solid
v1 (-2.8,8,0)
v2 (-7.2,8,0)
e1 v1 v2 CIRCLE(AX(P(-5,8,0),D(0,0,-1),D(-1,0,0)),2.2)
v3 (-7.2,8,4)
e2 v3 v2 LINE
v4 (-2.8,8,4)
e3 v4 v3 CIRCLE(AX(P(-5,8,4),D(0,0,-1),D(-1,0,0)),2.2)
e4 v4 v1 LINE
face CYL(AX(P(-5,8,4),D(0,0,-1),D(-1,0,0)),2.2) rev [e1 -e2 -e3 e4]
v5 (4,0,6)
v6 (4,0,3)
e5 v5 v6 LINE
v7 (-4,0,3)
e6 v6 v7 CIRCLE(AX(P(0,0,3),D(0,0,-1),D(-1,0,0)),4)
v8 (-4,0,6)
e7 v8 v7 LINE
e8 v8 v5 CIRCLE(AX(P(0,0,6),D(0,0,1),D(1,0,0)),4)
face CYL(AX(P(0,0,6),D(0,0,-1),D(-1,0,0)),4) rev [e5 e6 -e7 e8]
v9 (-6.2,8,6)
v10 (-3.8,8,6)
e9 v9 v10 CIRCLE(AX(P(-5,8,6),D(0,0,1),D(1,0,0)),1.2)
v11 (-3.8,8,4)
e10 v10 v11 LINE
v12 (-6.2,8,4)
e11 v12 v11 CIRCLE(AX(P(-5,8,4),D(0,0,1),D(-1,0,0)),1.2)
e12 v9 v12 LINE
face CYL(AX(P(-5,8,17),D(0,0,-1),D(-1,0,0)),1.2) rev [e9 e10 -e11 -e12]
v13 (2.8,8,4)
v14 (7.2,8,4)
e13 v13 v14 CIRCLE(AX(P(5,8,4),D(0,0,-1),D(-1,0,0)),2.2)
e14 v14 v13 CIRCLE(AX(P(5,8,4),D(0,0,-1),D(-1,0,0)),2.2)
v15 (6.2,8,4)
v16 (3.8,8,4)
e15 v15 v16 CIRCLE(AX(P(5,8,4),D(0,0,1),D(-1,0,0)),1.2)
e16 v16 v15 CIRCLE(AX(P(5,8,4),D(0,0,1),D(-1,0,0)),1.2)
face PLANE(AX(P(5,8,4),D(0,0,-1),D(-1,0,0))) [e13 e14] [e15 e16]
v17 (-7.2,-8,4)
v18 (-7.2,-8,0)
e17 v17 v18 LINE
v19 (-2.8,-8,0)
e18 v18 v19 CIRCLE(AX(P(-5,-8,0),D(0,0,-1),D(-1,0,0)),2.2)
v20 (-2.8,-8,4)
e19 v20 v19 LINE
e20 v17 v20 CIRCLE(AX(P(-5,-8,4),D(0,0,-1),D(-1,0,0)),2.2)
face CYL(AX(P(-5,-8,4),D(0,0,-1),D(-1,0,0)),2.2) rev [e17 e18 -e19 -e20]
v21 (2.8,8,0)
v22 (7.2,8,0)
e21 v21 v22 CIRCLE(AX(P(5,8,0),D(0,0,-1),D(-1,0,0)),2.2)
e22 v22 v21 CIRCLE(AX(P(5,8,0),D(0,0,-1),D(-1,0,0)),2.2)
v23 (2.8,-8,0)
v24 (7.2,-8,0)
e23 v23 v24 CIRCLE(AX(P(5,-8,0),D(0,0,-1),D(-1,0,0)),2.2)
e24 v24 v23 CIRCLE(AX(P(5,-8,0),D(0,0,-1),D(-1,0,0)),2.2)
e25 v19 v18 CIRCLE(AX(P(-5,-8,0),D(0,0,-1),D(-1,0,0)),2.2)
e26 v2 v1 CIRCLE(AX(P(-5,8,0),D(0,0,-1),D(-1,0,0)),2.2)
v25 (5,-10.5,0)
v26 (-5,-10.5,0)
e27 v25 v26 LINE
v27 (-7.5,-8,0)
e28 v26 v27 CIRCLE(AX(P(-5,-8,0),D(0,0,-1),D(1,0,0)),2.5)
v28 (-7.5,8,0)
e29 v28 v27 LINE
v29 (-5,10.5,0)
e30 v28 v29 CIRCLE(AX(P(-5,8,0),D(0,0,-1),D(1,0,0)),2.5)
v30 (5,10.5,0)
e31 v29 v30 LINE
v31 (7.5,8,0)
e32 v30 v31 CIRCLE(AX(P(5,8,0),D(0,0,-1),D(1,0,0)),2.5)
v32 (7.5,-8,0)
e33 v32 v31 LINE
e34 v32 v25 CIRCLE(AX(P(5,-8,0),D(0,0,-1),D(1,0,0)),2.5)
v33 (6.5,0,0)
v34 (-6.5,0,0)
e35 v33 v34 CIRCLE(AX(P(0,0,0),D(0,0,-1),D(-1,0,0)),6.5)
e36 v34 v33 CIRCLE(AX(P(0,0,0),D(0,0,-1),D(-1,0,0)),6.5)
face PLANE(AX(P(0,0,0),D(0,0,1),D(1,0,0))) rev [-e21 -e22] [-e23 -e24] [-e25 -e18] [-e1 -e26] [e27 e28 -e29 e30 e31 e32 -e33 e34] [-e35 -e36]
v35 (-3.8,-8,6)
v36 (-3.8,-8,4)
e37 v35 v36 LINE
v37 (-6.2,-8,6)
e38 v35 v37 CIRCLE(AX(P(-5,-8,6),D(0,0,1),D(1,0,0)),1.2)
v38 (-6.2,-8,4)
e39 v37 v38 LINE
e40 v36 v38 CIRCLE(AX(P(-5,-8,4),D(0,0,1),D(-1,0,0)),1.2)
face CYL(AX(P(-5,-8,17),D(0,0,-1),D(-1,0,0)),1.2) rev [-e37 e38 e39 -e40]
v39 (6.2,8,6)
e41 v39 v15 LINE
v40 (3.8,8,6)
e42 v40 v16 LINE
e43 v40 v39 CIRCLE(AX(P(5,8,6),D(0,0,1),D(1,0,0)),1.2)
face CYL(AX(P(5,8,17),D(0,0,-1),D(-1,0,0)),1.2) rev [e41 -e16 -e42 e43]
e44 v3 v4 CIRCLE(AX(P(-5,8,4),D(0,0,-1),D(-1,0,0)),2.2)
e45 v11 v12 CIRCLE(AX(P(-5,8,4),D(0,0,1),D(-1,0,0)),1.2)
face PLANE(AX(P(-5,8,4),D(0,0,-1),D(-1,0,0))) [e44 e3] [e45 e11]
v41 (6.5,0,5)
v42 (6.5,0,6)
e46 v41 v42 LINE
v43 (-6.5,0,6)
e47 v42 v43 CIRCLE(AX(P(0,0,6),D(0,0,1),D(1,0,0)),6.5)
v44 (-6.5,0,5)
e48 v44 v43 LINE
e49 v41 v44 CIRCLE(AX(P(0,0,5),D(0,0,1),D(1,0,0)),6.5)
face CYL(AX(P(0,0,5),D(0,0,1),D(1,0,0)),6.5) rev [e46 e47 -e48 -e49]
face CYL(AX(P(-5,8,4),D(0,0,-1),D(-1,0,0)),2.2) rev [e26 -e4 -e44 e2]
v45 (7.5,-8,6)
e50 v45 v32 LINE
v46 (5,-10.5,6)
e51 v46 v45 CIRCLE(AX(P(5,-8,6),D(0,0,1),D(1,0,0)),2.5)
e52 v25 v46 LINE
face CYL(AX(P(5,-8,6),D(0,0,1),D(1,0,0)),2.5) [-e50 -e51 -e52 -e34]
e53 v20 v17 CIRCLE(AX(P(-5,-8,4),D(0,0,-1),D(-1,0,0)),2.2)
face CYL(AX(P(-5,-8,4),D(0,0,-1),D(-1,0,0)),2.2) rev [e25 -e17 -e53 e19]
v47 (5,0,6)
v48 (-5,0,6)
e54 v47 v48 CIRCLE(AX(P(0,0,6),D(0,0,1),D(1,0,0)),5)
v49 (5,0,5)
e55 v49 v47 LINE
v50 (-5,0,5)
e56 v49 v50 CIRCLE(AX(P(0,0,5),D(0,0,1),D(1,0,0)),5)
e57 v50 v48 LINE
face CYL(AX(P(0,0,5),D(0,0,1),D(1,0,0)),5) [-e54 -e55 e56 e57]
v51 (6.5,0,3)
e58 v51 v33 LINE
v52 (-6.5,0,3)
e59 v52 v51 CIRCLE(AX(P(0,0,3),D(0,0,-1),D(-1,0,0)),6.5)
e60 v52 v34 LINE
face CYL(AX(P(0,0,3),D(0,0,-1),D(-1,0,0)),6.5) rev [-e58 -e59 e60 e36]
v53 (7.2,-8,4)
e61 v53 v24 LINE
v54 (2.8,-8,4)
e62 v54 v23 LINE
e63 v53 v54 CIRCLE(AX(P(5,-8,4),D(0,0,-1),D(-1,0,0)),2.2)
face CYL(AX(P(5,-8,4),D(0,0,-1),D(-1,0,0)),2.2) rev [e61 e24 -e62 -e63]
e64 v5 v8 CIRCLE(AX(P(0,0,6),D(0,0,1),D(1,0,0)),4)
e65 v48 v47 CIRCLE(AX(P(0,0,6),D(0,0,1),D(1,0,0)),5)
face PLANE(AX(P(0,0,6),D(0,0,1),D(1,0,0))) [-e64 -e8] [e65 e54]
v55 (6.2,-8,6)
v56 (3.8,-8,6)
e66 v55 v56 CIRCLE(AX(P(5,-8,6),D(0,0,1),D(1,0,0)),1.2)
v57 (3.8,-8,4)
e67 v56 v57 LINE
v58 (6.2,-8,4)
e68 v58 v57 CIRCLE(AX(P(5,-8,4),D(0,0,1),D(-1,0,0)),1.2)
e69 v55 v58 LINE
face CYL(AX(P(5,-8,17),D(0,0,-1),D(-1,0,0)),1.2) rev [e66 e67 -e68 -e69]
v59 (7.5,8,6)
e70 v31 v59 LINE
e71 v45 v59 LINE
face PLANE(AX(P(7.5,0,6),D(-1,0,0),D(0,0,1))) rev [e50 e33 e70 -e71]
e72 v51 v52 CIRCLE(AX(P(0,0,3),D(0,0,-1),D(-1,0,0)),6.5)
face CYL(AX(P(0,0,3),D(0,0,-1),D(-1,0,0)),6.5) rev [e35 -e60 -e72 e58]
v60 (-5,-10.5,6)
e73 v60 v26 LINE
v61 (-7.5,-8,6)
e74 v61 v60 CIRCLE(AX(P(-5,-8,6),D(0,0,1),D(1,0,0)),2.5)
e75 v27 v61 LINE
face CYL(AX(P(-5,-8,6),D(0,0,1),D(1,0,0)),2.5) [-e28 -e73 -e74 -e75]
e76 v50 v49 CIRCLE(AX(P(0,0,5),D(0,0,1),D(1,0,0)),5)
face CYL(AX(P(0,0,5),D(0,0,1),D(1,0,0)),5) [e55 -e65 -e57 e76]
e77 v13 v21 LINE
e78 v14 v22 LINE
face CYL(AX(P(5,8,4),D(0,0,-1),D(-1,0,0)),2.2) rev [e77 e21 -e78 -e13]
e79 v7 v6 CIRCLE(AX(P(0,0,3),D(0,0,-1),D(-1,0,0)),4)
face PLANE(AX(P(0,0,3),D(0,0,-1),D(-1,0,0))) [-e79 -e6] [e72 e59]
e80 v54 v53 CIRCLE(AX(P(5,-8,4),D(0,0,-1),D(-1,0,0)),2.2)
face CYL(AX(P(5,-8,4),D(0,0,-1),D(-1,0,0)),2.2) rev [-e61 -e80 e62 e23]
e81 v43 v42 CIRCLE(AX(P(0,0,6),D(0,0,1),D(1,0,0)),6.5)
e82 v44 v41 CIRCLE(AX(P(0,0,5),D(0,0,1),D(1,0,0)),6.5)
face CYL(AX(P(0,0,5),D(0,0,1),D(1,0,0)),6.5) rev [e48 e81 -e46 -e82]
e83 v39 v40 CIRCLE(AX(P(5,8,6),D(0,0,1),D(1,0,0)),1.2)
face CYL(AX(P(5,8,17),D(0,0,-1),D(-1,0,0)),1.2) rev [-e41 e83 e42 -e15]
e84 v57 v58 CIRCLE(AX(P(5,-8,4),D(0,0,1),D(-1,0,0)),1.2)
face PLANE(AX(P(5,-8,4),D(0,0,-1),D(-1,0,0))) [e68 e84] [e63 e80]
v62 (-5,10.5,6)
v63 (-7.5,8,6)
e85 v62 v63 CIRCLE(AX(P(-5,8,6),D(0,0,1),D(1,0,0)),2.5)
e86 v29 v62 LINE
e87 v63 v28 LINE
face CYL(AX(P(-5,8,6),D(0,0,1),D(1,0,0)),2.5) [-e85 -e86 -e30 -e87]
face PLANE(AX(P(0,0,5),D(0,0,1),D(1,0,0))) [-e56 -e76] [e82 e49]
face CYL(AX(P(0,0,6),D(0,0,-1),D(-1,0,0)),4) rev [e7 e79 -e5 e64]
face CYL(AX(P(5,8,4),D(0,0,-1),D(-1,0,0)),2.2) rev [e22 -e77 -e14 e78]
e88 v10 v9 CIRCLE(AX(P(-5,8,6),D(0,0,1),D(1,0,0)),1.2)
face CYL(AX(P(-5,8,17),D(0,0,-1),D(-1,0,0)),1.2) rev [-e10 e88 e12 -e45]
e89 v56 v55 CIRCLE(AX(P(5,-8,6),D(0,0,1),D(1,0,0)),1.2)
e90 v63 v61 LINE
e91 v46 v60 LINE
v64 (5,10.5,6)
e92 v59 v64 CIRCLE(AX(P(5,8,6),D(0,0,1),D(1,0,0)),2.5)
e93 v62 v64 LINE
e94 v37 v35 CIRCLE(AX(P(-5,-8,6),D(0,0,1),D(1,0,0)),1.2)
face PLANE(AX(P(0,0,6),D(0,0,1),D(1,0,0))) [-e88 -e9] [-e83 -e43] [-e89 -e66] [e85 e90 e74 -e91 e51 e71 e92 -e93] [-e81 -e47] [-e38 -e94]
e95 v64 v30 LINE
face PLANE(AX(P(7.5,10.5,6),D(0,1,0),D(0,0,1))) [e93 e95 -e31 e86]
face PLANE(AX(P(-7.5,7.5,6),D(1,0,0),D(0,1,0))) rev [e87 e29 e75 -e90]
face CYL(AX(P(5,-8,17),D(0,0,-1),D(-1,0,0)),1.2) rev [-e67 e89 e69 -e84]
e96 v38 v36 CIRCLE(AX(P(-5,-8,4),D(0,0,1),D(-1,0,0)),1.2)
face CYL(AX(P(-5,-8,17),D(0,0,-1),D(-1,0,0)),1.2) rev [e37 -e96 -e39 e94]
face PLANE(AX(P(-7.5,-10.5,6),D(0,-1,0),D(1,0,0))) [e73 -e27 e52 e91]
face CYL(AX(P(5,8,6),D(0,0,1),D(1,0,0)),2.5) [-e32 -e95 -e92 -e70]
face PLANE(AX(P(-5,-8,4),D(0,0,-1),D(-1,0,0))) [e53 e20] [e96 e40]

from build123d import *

# Parameters (mm, degrees)
SKETCH1_R           = 4
BOSS_EXTRUDE1_DEPTH = 6
SKETCH3_R           = 6.5
CUT_EXTRUDE2_DEPTH  = 3
CUT_EXTRUDE3_START  = -1
SKETCH4_R           = 6.5
SKETCH4_R_2         = 5
CUT_EXTRUDE3_DEPTH  = 1
SKETCH5_W           = 15
SKETCH5_H           = 3
BOSS_EXTRUDE2_DEPTH = 6
SKETCH6_R           = 1.2
CUT_EXTRUDE7_DEPTH  = 17
FILLET3_R           = 2.5
SKETCH7_R           = 2.2
CUT_EXTRUDE8_DEPTH  = 4


with BuildPart() as part:
    # Sketch1 → Boss-Extrude1 (new body)
    with BuildSketch(Plane.XY):
        Polygon((7.5, 0), (7.5, 7.5), (-7.5, 7.5), (-7.5, -7.5), (7.5, -7.5), align=None)
        Circle(SKETCH1_R, mode=Mode.SUBTRACT)
    extrude(amount=BOSS_EXTRUDE1_DEPTH)

    # Sketch3 → Cut-Extrude2 (cut)
    with BuildSketch(Plane(origin=(0, 0, 0), x_dir=(-1, 0, 0), z_dir=(0, 0, -1))):
        Circle(SKETCH3_R)
    extrude(amount=-CUT_EXTRUDE2_DEPTH, mode=Mode.SUBTRACT)

    # Sketch4 → Cut-Extrude3 (cut)
    with BuildSketch(Plane.XY.offset(6).offset(CUT_EXTRUDE3_START)):
        with Locations(Location((0, 0, 0), (0, 0, 180))):
            Circle(SKETCH4_R)
        Circle(SKETCH4_R_2, mode=Mode.SUBTRACT)
    extrude(amount=CUT_EXTRUDE3_DEPTH, mode=Mode.SUBTRACT)

    # Sketch5 → Boss-Extrude2 (add)
    with BuildSketch(Plane(origin=(0, 0, 0), x_dir=(-1, 0, 0), z_dir=(0, 0, -1))):
        with Locations((0, -9)):
            Rectangle(SKETCH5_W, SKETCH5_H)
        with Locations((0, 9)):
            Rectangle(SKETCH5_W, SKETCH5_H)
    extrude(amount=-BOSS_EXTRUDE2_DEPTH)

    # Sketch6 → Cut-Extrude7 (cut)
    with BuildSketch(Plane(origin=(0, 0, 0), x_dir=(-1, 0, 0), z_dir=(0, 0, -1))):
        with Locations((5, 8)):
            Circle(SKETCH6_R)
        with Locations((-5, 8)):
            Circle(SKETCH6_R)
        with Locations((-5, -8)):
            Circle(SKETCH6_R)
        with Locations((5, -8)):
            Circle(SKETCH6_R)
    extrude(amount=-CUT_EXTRUDE7_DEPTH, mode=Mode.SUBTRACT)

    # Fillet3
    fillet3_edges = [part.edges().sort_by_distance(p)[0] for p in [
        (-7.5, -10.5, 3),
        (7.5, -10.5, 3),
        (7.5, 10.5, 3),
        (-7.5, 10.5, 3),
    ]]
    fillet(fillet3_edges, radius=FILLET3_R)

    # Sketch7 → Cut-Extrude8 (cut)
    with BuildSketch(Plane(origin=(0, 0, 0), x_dir=(-1, 0, 0), z_dir=(0, 0, -1))):
        with Locations((-5, -8)):
            Circle(SKETCH7_R)
        with Locations((-5, 8)):
            Circle(SKETCH7_R)
        with Locations((5, 8)):
            Circle(SKETCH7_R)
        with Locations((5, -8)):
            Circle(SKETCH7_R)
    extrude(amount=-CUT_EXTRUDE8_DEPTH, mode=Mode.SUBTRACT)


solid = part.part
